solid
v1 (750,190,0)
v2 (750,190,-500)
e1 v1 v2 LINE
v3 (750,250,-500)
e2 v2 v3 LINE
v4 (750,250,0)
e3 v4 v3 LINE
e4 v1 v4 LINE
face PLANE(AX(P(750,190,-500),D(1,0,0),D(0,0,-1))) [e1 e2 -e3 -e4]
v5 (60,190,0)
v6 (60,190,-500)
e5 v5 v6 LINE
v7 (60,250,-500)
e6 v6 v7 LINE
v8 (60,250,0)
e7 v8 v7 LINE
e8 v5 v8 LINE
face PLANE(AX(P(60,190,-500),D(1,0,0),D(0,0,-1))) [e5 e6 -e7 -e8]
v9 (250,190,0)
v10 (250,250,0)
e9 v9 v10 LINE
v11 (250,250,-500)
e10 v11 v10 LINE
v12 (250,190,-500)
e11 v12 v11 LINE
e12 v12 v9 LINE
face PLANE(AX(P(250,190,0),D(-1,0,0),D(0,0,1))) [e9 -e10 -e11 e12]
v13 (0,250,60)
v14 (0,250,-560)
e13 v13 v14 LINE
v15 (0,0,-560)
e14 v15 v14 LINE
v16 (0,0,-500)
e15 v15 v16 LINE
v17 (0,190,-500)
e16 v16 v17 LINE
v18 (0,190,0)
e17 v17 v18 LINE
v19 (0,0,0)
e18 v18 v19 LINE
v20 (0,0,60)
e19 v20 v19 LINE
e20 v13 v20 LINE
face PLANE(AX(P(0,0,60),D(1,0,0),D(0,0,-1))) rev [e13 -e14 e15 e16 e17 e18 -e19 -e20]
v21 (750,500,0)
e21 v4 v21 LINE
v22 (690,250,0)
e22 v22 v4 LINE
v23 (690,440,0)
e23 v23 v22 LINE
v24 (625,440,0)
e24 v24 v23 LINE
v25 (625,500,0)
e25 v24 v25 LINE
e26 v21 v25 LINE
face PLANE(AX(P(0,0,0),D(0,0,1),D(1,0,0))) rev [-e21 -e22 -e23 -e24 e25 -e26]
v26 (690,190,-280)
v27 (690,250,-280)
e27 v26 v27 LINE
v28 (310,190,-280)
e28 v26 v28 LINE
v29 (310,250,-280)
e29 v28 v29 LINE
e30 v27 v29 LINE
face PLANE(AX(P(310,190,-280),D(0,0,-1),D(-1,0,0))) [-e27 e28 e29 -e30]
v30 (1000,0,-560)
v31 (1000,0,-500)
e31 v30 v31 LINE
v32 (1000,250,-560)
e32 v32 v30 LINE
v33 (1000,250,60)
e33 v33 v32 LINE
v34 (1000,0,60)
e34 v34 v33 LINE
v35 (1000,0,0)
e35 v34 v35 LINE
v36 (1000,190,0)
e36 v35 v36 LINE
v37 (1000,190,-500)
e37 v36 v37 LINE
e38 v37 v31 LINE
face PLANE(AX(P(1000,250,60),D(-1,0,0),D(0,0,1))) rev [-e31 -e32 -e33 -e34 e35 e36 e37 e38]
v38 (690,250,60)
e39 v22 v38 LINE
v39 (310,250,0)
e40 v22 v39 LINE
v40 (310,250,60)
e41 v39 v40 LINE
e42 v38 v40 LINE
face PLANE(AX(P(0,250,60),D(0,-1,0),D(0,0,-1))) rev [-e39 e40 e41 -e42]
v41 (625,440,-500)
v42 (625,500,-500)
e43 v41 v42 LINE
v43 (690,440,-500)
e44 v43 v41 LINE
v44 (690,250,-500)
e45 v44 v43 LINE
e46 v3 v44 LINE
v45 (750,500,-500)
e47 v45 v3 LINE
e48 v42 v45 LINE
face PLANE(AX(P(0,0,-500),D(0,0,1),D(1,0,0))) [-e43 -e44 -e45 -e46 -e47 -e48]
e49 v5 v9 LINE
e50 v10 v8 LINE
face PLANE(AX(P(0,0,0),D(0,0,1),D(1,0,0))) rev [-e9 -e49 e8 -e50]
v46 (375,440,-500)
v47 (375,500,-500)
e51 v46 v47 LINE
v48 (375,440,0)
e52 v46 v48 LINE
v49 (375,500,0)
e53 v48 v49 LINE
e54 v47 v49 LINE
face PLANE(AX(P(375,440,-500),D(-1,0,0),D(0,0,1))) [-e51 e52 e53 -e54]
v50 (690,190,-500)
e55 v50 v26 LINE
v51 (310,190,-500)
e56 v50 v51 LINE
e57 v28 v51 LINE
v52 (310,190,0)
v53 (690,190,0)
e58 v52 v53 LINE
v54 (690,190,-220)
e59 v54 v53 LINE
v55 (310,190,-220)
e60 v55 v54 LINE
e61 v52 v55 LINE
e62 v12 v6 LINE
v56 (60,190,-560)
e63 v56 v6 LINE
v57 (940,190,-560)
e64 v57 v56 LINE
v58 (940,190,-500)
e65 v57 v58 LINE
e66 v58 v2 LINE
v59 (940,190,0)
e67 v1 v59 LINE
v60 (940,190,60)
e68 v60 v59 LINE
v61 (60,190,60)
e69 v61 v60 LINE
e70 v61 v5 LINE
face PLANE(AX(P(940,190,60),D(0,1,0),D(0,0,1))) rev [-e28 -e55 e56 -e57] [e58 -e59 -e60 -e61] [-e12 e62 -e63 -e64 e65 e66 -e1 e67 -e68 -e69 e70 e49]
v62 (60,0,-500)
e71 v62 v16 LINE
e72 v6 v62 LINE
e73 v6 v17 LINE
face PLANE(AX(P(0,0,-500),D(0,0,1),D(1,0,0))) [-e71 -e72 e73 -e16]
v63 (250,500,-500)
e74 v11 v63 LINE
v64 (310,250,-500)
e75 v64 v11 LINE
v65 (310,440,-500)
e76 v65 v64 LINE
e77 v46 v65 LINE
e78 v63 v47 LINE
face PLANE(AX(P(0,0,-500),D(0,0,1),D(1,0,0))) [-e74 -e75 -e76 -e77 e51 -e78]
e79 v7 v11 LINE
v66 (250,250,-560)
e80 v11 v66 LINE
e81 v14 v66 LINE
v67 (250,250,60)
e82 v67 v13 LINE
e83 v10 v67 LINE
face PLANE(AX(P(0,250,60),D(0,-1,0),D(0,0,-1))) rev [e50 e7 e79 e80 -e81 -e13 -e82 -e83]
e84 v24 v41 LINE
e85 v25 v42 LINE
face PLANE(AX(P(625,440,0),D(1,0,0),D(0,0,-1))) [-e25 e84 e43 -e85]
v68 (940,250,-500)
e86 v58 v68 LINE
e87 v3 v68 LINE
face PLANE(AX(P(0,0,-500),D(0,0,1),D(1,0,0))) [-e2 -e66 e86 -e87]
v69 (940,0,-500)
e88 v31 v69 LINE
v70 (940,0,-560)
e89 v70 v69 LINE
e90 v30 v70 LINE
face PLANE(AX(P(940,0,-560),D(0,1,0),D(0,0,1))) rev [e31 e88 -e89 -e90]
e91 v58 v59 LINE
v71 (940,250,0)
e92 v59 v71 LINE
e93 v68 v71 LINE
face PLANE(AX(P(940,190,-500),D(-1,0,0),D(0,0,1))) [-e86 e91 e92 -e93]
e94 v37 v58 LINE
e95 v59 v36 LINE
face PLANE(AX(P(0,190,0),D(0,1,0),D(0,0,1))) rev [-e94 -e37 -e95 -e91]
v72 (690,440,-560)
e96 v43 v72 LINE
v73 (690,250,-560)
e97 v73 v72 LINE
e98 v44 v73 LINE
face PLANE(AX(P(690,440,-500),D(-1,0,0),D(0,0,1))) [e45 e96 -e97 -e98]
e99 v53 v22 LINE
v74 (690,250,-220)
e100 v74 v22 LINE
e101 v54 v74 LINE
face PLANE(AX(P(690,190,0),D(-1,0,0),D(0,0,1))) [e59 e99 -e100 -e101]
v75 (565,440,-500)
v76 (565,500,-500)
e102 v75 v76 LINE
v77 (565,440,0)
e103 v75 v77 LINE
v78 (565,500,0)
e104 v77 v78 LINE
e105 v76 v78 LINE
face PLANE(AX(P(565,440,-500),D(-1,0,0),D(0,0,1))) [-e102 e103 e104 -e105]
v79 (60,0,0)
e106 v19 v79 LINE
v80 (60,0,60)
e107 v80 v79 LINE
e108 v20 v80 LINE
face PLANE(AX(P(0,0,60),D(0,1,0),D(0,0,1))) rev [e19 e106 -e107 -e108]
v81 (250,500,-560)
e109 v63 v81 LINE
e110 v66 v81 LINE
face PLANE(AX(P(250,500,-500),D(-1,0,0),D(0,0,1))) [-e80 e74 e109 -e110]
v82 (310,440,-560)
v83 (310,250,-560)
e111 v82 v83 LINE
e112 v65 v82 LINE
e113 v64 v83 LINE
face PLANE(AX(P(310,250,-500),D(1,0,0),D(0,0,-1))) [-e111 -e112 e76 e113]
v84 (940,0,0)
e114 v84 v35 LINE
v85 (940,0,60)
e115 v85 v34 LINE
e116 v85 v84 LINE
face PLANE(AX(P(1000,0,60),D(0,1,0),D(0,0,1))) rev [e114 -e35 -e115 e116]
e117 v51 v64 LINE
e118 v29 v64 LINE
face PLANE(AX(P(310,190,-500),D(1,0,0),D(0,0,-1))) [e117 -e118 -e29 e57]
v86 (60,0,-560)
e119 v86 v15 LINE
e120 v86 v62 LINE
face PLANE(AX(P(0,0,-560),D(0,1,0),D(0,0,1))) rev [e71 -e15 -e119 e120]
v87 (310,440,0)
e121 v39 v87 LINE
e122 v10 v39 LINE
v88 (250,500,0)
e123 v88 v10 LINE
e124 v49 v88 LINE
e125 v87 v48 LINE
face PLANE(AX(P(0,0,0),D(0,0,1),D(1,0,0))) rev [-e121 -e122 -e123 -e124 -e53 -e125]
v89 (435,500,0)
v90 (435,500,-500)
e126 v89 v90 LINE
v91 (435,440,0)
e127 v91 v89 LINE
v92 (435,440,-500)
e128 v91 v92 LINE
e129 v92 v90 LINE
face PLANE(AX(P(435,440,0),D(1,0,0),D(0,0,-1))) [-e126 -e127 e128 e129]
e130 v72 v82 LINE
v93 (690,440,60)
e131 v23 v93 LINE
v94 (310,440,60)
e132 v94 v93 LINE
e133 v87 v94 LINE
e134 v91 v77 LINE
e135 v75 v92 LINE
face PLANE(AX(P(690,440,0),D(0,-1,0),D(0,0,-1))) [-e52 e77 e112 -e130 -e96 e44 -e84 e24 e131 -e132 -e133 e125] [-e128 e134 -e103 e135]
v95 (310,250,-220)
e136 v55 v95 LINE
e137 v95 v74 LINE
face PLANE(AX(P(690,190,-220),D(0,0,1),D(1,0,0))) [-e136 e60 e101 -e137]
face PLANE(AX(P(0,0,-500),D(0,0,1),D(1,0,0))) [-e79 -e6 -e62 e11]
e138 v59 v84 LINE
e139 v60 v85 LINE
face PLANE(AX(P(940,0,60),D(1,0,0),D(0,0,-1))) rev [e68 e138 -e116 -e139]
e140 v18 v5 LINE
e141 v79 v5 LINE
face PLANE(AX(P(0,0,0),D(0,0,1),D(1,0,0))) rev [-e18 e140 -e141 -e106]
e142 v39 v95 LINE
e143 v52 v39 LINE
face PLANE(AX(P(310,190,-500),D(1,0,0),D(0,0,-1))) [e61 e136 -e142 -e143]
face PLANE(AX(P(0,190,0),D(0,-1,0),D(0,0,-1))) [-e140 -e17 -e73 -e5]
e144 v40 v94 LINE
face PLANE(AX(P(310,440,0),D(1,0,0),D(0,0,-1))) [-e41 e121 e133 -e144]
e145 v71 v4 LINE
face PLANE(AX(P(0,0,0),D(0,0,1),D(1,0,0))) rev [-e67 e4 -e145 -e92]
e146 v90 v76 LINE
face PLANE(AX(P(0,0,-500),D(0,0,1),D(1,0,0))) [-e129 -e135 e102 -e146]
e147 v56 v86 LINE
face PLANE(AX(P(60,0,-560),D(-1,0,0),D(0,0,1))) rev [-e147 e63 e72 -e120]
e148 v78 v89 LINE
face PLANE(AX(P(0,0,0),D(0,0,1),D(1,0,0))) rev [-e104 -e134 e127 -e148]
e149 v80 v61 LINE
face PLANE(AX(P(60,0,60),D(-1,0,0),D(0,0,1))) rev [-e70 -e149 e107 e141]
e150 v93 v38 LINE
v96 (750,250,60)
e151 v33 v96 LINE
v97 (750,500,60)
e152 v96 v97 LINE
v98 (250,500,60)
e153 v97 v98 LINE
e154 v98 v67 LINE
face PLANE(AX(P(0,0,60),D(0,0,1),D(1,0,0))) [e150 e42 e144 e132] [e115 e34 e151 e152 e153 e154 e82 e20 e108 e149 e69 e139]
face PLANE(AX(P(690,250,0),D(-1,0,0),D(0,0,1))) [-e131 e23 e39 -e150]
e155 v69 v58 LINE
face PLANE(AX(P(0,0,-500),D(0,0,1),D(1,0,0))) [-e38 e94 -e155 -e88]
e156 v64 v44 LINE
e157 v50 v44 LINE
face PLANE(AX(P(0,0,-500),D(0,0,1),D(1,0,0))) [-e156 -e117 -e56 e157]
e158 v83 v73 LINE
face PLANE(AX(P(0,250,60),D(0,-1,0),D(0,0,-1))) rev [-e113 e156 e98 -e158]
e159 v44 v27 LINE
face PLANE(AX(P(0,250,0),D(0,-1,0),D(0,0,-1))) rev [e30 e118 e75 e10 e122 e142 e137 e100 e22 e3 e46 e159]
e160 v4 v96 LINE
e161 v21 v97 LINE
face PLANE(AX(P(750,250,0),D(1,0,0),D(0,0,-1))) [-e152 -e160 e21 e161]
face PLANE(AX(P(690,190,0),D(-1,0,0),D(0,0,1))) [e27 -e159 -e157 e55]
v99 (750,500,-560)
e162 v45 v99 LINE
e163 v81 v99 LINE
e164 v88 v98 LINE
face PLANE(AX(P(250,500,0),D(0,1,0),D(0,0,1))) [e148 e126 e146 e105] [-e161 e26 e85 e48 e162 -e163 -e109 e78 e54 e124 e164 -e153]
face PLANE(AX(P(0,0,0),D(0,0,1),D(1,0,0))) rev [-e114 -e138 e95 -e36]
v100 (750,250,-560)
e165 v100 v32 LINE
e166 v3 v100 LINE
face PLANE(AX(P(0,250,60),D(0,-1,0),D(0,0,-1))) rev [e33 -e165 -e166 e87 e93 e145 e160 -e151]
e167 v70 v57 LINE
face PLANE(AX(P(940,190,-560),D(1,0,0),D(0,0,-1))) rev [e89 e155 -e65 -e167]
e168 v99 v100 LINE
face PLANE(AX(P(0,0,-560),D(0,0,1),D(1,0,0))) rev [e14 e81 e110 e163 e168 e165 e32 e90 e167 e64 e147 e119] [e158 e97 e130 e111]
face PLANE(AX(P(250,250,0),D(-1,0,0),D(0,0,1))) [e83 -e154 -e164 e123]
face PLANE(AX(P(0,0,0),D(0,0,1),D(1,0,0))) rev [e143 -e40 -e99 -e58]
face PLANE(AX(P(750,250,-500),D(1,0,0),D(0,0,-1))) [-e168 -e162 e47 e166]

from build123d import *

# Parameters (mm, degrees)
FRONT_FRAME_DEPTH       = 60
FRAME_MEMBER_2_SKETCH_W = 60
FRAME_MEMBER_2_SKETCH_H = 500
FRAME_MEMBER_2_DEPTH    = 60
FRAME_MEMBER_3_DEPTH    = 60
FRAME_MEMBER_4_DEPTH    = 60
FRAME_MEMBER_5_DEPTH    = 60
FRAME_MEMBER_6_SKETCH_W = 60
FRAME_MEMBER_6_SKETCH_H = 500
FRAME_MEMBER_6_DEPTH    = 60
FRAME_MEMBER_7_DEPTH    = 60
FRAME_MEMBER_8_SKETCH_W = 60
FRAME_MEMBER_8_SKETCH_H = 500
FRAME_MEMBER_8_DEPTH    = 60


with BuildPart() as part:
    # Front Frame Sketch → Front Frame (new body)
    with BuildSketch(Plane.XY):
        Polygon((0, 0), (0, 250), (1000, 250), (1000, 0), (940, 0), (940, 190), (60, 190), (60, 0), align=None)
    extrude(amount=FRONT_FRAME_DEPTH)

    # Frame Member 2 Sketch → Frame Member 2 (add)
    with BuildSketch(Plane(origin=(0, 250, 0), x_dir=(1, 0, 0), z_dir=(0, 1, 0))):
        with Locations((30, 250)):
            Rectangle(FRAME_MEMBER_2_SKETCH_W, FRAME_MEMBER_2_SKETCH_H)
        with Locations((970, 250)):
            Rectangle(FRAME_MEMBER_2_SKETCH_W, FRAME_MEMBER_2_SKETCH_H)
    extrude(amount=-FRAME_MEMBER_2_DEPTH)

    # Frame Member 3 Sketch → Frame Member 3 (add)
    with BuildSketch(Plane(origin=(0, 0, -500), x_dir=(-1, 0, 0), z_dir=(0, 0, -1))):
        Polygon((-1000, 250), (0, 250), (0, 0), (-60, 0), (-60, 190), (-940, 190), (-940, 0), (-1000, 0), align=None)
    extrude(amount=FRAME_MEMBER_3_DEPTH)

    # Frame Member 4 Sketch → Frame Member 4 (add)
    with BuildSketch(Plane.XY.offset(60)):
        Polygon((750, 250), (750, 500), (250, 500), (250, 250), (310, 250), (310, 440), (690, 440), (690, 250), align=None)
    extrude(amount=-FRAME_MEMBER_4_DEPTH)

    # Frame Member 5 Sketch → Frame Member 5 (add)
    with BuildSketch(Plane(origin=(0, 0, -560), x_dir=(-1, 0, 0), z_dir=(0, 0, -1))):
        Polygon((-750, 250), (-750, 500), (-250, 500), (-250, 250), (-310, 250), (-310, 440), (-690, 440), (-690, 250), align=None)
    extrude(amount=-FRAME_MEMBER_5_DEPTH)

    # Frame Member 6 Sketch → Frame Member 6 (add)
    with BuildSketch(Plane(origin=(0, 250, 0), x_dir=(1, 0, 0), z_dir=(0, 1, 0))):
        with Locations((280, 250)):
            Rectangle(FRAME_MEMBER_6_SKETCH_W, FRAME_MEMBER_6_SKETCH_H)
        with Locations((720, 250)):
            Rectangle(FRAME_MEMBER_6_SKETCH_W, FRAME_MEMBER_6_SKETCH_H)
    extrude(amount=-FRAME_MEMBER_6_DEPTH)

    # Frame Member 7 Sketch → Frame Member 7 (add)
    with BuildSketch(Plane(origin=(0, 250, 0), x_dir=(1, 0, 0), z_dir=(0, 1, 0))):
        Polygon((310, 250), (310, 280), (690, 280), (690, 220), (310, 220), align=None)
    extrude(amount=-FRAME_MEMBER_7_DEPTH)

    # Frame Member 8 Sketch → Frame Member 8 (add)
    with BuildSketch(Plane(origin=(0, 500, 0), x_dir=(1, 0, 0), z_dir=(0, 1, 0))):
        with Locations((405, 250)):
            Rectangle(FRAME_MEMBER_8_SKETCH_W, FRAME_MEMBER_8_SKETCH_H)
        with Locations((595, 250)):
            Rectangle(FRAME_MEMBER_8_SKETCH_W, FRAME_MEMBER_8_SKETCH_H)
    extrude(amount=-FRAME_MEMBER_8_DEPTH)


solid = part.part
